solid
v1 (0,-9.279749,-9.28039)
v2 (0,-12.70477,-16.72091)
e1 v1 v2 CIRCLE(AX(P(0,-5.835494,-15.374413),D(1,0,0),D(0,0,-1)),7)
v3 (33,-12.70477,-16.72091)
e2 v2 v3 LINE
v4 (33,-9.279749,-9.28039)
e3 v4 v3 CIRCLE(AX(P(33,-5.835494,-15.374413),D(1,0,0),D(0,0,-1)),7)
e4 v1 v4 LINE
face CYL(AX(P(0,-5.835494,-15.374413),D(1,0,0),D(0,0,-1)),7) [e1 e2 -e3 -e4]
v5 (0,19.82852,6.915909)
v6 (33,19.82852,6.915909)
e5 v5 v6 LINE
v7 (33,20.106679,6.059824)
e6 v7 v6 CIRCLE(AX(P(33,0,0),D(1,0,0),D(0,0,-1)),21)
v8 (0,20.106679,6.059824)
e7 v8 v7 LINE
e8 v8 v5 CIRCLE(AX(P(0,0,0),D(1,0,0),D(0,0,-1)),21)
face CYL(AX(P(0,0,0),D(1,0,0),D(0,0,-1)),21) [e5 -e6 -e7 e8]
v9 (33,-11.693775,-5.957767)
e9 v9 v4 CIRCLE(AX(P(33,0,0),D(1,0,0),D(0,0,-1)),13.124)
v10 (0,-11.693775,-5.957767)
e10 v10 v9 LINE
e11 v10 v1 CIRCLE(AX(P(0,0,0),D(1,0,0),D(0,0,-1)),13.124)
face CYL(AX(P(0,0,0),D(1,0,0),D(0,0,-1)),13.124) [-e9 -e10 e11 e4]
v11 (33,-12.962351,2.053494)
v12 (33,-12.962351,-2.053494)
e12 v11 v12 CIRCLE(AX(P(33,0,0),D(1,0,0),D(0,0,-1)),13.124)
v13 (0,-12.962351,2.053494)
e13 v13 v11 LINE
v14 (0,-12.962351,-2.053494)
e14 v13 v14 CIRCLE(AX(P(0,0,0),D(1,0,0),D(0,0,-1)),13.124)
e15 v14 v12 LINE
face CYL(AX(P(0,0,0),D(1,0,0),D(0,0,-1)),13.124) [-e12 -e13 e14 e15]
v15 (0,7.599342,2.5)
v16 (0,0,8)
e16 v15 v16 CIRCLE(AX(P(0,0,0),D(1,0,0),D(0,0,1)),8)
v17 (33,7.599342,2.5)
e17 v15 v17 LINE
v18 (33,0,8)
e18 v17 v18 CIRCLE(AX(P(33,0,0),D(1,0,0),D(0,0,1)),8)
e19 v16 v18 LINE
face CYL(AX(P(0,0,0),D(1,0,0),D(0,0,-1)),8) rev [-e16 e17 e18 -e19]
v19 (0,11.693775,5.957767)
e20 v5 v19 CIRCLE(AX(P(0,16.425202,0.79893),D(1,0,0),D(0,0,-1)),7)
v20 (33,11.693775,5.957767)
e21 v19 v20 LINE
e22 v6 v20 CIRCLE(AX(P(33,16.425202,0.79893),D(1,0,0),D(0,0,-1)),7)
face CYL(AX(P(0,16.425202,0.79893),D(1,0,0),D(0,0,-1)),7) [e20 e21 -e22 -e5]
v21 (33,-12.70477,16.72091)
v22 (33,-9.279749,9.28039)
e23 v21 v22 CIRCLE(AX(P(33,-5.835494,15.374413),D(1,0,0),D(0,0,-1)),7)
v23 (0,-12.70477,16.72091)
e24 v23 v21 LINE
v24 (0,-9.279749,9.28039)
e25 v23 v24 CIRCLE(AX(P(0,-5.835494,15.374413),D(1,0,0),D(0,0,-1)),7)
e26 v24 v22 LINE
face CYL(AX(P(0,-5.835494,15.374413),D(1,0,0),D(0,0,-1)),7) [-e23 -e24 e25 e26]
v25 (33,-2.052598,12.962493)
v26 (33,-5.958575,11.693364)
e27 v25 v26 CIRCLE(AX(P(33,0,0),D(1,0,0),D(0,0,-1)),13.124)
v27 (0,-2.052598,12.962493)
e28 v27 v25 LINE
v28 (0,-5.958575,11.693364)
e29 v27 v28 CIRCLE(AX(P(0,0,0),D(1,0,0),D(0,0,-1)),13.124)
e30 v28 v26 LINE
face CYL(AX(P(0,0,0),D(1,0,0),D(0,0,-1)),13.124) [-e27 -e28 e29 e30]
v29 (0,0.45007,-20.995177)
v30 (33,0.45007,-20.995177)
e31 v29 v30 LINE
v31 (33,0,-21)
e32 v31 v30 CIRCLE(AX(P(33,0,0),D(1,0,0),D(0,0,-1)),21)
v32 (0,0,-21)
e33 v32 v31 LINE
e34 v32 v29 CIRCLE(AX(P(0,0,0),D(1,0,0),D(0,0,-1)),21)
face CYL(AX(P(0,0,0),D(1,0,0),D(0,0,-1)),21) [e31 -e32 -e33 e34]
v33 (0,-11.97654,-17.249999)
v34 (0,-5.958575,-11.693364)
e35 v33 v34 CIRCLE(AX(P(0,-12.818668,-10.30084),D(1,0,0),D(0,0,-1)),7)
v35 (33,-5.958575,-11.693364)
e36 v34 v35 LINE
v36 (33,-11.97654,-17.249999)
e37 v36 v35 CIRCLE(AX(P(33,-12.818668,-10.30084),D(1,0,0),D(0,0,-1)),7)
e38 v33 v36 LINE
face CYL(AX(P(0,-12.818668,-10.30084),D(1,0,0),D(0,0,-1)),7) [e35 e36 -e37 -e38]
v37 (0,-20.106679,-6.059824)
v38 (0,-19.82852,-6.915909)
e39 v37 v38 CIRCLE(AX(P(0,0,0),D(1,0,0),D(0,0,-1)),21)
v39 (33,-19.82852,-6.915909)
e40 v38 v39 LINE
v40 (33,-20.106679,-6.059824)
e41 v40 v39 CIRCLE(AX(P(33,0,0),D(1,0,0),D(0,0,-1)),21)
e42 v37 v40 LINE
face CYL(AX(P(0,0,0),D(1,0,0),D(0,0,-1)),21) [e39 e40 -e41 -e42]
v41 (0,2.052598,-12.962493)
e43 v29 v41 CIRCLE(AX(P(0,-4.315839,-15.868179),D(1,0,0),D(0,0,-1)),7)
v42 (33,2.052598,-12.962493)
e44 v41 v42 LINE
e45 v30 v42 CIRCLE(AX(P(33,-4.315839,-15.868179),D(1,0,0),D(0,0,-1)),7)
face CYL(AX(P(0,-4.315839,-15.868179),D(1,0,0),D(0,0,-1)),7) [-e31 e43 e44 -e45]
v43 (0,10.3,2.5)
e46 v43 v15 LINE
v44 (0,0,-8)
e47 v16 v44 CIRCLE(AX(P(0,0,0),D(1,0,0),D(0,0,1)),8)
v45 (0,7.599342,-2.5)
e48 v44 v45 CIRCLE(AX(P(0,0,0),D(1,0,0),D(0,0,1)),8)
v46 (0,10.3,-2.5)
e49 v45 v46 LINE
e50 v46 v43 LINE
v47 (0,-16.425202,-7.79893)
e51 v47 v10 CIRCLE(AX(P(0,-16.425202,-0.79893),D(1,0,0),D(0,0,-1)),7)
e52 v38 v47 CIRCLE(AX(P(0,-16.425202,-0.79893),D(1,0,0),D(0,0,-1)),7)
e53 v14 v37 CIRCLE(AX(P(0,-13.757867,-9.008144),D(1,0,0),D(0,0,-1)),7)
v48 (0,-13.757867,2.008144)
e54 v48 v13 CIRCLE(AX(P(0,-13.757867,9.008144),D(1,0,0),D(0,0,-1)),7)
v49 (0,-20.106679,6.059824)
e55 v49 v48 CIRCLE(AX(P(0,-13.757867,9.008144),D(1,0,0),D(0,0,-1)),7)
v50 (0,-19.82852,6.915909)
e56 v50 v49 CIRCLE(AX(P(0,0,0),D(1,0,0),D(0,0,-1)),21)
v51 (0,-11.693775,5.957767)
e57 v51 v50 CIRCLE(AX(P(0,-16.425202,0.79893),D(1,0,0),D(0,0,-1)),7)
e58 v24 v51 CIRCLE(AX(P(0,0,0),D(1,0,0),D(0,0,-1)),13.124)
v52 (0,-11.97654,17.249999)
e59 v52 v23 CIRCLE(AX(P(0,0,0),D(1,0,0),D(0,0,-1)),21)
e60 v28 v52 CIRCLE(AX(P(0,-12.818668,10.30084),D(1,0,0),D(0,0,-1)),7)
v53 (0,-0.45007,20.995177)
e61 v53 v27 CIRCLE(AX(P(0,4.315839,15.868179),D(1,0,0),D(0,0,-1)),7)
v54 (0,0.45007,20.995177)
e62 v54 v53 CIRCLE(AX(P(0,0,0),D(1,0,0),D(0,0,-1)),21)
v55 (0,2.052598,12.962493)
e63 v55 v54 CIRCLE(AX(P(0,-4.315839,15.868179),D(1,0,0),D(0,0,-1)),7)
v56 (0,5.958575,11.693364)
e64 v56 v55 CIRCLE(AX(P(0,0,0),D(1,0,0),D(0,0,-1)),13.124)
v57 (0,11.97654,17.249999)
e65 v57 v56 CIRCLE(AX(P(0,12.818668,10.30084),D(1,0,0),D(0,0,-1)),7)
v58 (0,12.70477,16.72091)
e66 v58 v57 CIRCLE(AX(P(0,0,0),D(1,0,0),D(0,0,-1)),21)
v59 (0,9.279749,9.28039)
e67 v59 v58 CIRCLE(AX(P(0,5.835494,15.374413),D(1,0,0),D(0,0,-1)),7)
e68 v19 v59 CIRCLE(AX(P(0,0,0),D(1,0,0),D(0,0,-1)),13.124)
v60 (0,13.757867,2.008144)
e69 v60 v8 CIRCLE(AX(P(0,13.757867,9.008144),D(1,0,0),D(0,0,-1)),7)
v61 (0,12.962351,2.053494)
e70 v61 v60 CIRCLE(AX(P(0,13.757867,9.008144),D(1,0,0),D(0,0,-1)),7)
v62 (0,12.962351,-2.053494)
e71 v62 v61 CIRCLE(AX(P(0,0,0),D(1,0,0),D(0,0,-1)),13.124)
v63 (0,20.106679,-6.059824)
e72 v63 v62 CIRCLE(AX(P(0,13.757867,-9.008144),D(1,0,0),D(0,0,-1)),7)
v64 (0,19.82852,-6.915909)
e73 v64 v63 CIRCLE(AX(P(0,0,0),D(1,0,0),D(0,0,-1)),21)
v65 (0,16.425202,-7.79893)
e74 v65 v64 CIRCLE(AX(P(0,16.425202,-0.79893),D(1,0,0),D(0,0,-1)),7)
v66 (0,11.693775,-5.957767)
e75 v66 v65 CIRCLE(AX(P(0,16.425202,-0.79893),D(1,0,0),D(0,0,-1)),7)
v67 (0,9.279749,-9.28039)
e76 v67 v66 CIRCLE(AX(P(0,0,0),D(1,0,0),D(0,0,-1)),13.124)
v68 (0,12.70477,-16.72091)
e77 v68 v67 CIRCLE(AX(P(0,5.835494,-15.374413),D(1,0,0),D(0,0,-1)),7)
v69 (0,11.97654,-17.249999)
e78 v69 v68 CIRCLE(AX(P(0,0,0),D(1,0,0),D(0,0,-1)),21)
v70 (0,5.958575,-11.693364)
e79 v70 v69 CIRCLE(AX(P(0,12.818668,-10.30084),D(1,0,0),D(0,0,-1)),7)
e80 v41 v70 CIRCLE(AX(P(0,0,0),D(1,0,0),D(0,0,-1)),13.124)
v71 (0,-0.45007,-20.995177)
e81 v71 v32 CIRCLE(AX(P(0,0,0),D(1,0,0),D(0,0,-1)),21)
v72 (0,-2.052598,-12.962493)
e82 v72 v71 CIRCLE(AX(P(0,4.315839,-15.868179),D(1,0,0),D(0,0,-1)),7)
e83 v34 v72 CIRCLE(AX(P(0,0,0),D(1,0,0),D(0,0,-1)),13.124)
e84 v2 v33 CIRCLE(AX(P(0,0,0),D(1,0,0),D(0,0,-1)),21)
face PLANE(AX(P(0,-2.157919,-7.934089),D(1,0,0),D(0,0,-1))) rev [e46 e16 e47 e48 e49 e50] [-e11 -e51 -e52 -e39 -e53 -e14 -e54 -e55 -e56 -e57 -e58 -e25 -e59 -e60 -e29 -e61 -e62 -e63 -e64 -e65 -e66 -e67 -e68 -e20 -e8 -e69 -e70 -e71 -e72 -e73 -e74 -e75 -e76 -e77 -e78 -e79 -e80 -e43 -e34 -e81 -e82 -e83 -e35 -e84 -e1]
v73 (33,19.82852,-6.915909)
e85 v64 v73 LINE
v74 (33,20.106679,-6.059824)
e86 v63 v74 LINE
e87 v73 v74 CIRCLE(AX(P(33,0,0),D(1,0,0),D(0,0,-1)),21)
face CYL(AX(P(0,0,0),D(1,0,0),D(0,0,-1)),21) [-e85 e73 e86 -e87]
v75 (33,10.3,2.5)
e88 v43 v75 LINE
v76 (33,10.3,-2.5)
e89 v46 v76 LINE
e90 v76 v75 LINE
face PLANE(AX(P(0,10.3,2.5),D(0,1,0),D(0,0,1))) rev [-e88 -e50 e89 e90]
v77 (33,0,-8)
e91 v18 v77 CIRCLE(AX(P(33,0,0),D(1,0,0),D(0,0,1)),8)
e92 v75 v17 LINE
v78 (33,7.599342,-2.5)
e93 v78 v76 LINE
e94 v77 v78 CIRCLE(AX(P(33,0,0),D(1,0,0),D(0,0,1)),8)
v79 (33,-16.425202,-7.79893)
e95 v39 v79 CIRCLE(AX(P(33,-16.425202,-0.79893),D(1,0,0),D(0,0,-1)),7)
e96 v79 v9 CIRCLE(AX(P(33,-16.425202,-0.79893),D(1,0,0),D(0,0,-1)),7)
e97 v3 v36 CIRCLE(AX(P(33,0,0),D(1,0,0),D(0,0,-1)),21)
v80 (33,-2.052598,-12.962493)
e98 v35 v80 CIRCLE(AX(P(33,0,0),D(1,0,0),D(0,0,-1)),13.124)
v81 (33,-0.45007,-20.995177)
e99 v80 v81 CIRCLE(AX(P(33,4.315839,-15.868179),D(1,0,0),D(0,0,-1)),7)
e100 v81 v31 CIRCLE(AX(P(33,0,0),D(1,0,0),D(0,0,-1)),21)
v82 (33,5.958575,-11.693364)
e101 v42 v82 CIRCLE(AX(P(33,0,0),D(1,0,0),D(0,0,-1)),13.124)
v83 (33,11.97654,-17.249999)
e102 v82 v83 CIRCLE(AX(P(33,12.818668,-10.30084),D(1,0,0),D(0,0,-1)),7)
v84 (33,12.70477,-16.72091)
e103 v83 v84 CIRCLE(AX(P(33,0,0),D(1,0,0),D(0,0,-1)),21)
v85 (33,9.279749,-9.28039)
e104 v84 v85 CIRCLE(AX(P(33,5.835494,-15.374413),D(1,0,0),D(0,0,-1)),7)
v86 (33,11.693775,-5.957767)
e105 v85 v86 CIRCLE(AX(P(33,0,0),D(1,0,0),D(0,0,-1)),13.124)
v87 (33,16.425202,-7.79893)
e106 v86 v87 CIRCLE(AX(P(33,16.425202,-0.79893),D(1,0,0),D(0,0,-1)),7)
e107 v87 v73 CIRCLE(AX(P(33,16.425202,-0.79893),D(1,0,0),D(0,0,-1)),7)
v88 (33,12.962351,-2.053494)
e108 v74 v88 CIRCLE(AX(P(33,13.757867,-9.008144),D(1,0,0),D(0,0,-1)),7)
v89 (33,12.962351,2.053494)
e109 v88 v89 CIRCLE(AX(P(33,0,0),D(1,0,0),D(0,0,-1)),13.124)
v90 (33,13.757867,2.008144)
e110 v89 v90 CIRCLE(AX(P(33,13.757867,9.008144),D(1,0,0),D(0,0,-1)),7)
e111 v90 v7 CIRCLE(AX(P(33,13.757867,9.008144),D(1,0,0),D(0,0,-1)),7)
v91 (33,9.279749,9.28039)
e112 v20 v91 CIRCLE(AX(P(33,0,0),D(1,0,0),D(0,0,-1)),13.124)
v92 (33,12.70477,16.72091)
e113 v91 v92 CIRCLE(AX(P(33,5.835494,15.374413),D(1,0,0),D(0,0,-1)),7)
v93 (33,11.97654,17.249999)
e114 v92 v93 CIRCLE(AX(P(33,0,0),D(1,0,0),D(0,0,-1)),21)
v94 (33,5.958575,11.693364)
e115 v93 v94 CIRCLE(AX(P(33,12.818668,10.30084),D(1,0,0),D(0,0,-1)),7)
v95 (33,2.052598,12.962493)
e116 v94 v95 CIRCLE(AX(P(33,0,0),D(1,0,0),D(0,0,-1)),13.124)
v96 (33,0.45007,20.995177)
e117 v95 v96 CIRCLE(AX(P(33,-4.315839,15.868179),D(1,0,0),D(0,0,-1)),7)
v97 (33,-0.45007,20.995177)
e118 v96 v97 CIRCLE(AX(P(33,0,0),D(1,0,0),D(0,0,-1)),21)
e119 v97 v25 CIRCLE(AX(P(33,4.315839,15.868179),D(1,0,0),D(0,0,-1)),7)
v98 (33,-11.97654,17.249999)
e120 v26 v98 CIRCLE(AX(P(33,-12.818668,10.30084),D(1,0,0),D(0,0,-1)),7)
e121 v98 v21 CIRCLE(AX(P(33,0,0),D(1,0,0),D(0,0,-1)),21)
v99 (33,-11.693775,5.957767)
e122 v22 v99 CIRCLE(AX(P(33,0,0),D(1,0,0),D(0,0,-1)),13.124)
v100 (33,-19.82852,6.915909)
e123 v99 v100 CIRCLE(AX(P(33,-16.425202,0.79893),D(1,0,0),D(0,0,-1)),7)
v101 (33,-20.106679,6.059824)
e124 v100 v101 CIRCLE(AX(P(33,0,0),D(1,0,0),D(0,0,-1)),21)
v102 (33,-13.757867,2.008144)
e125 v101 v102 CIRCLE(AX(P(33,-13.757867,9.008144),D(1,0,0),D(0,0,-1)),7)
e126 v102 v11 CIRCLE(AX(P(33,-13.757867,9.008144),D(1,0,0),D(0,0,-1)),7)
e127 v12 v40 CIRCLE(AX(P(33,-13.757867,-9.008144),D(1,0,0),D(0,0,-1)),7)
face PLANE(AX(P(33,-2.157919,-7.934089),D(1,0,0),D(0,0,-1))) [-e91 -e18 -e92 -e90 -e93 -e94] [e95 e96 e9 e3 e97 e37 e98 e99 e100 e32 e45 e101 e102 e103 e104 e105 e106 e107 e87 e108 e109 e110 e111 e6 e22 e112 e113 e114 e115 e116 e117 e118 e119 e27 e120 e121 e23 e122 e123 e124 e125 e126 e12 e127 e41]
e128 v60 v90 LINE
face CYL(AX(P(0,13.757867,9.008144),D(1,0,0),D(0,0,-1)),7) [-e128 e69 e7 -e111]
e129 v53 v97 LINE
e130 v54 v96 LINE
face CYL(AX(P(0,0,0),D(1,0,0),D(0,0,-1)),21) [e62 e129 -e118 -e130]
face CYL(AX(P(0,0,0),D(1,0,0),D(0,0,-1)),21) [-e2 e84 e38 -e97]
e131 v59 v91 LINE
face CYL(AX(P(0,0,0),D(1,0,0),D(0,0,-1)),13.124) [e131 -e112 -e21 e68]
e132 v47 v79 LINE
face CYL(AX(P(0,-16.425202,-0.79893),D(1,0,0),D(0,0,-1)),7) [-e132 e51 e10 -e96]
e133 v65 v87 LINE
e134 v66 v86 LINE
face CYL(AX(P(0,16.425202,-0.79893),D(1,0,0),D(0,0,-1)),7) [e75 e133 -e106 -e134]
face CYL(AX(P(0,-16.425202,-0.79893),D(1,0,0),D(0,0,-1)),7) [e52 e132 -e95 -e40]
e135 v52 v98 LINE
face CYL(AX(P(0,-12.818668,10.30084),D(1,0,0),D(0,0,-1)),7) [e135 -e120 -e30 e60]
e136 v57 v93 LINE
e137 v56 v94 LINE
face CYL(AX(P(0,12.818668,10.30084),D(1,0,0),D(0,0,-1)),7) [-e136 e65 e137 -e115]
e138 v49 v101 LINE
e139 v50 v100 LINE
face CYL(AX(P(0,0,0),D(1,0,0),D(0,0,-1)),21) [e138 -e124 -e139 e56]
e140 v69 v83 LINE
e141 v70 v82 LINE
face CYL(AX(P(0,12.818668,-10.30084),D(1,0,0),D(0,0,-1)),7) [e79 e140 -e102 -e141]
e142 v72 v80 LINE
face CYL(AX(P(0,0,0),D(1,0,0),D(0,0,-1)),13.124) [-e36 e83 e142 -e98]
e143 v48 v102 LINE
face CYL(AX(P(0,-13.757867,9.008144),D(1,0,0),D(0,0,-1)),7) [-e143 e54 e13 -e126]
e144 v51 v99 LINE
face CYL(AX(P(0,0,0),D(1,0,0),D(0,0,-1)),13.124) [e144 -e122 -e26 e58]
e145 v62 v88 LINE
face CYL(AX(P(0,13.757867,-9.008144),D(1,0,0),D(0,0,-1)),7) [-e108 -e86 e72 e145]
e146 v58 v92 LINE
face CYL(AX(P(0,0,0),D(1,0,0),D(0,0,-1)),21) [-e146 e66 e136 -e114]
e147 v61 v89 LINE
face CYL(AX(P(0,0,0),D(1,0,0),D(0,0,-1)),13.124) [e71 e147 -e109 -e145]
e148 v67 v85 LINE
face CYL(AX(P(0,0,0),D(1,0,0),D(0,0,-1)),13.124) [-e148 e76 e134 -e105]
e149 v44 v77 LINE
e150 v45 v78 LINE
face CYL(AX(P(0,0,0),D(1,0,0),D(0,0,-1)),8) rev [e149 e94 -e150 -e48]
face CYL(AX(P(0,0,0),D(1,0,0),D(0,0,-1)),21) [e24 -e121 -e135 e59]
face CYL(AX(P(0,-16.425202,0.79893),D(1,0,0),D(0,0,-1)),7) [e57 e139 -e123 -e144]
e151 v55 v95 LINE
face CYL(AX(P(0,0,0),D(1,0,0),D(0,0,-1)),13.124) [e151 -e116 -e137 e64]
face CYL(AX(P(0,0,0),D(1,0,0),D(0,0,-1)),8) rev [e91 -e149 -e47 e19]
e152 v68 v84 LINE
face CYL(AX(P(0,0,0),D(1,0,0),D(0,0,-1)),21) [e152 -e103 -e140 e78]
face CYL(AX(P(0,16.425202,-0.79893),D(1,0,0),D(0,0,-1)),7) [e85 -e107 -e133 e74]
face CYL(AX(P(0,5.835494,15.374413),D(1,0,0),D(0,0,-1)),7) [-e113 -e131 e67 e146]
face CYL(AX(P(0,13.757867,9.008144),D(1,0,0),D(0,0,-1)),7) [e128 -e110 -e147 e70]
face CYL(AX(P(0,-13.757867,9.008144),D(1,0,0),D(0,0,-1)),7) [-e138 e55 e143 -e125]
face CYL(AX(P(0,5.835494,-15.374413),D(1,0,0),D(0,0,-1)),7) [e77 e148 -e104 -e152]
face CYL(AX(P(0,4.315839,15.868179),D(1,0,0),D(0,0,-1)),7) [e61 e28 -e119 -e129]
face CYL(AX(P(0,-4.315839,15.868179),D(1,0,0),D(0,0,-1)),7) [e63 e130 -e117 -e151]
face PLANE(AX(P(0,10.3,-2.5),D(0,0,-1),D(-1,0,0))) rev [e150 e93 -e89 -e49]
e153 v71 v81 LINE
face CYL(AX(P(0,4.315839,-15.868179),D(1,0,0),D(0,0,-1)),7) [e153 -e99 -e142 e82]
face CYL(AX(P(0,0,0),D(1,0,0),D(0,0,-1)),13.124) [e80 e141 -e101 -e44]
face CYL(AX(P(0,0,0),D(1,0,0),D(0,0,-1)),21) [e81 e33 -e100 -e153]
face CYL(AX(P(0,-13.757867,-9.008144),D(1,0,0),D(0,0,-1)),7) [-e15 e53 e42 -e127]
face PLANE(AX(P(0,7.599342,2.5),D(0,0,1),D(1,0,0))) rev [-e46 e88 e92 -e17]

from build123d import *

# Parameters (mm, degrees)
BOSS_EXTRUDE1_DEPTH = 33


with BuildPart() as part:
    # Sketch1 → Boss-Extrude1 (new body)
    with BuildSketch(Plane(origin=(33, 0, 0), x_dir=(0, 0, -1), z_dir=(1, 0, 0))):
        with BuildLine():
            ThreePointArc((20.995176507, 0.450070465), (17.237696927, 2.548883943), (12.962492698, 2.05259812))
            ThreePointArc((12.962492698, 2.05259812), (12.48166572, 4.055539034), (11.693363786, 5.958575279))
            ThreePointArc((11.693363786, 5.958575279), (15.443786149, 8.06997361), (17.249999376, 11.976540465))
            ThreePointArc((17.249999376, 11.976540465), (16.989356882, 12.343490298), (16.720909812, 12.704769776))
            ThreePointArc((16.720909812, 12.704769776), (12.447393366, 12.194154464), (9.280389979, 9.279748803))
            ThreePointArc((9.280389979, 9.279748803), (7.714093651, 10.617539034), (5.957767351, 11.693775447))
            ThreePointArc((5.957767351, 11.693775447), (7.750873978, 15.606375533), (6.91590879, 19.828520006))
            ThreePointArc((6.91590879, 19.828520006), (6.489356882, 19.972186842), (6.059823892, 20.106678851))
            ThreePointArc((6.059823892, 20.106678851), (2.902608611, 17.181672443), (2.053493716, 12.96235085))
            ThreePointArc((2.053493716, 12.96235085), (0, 13.124), (-2.053493716, 12.96235085))
            ThreePointArc((-2.053493716, 12.96235085), (-2.902608611, 17.181672443), (-6.059823892, 20.106678851))
            ThreePointArc((-6.059823892, 20.106678851), (-6.489356882, 19.972186842), (-6.91590879, 19.828520006))
            ThreePointArc((-6.91590879, 19.828520006), (-7.750873978, 15.606375533), (-5.957767351, 11.693775447))
            ThreePointArc((-5.957767351, 11.693775447), (-7.714093651, 10.617539034), (-9.280389979, 9.279748803))
            ThreePointArc((-9.280389979, 9.279748803), (-12.447393366, 12.194154464), (-16.720909812, 12.704769776))
            ThreePointArc((-16.720909812, 12.704769776), (-16.989356882, 12.343490298), (-17.249999376, 11.976540465))
            ThreePointArc((-17.249999376, 11.976540465), (-15.443786149, 8.06997361), (-11.693363786, 5.958575279))
            ThreePointArc((-11.693363786, 5.958575279), (-12.48166572, 4.055539034), (-12.962492698, 2.05259812))
            ThreePointArc((-12.962492698, 2.05259812), (-17.237696927, 2.548883943), (-20.995176507, 0.450070465))
            ThreePointArc((-20.995176507, 0.450070465), (-21, 0), (-20.995176507, -0.450070465))
            ThreePointArc((-20.995176507, -0.450070465), (-17.237696927, -2.548883943), (-12.962492698, -2.05259812))
            ThreePointArc((-12.962492698, -2.05259812), (-12.48166572, -4.055539034), (-11.693363786, -5.958575279))
            ThreePointArc((-11.693363786, -5.958575279), (-15.443786149, -8.06997361), (-17.249999376, -11.976540465))
            ThreePointArc((-17.249999376, -11.976540465), (-16.989356882, -12.343490298), (-16.720909812, -12.704769776))
            ThreePointArc((-16.720909812, -12.704769776), (-12.447393366, -12.194154464), (-9.280389979, -9.279748803))
            ThreePointArc((-9.280389979, -9.279748803), (-7.714093651, -10.617539034), (-5.957767351, -11.693775447))
            ThreePointArc((-5.957767351, -11.693775447), (-7.750873978, -15.606375533), (-6.91590879, -19.828520006))
            ThreePointArc((-6.91590879, -19.828520006), (-6.489356882, -19.972186842), (-6.059823892, -20.106678851))
            ThreePointArc((-6.059823892, -20.106678851), (-2.902608611, -17.181672443), (-2.053493716, -12.96235085))
            ThreePointArc((-2.053493716, -12.96235085), (0, -13.124), (2.053493716, -12.96235085))
            ThreePointArc((2.053493716, -12.96235085), (2.902608611, -17.181672443), (6.059823892, -20.106678851))
            ThreePointArc((6.059823892, -20.106678851), (6.489356882, -19.972186842), (6.91590879, -19.828520006))
            ThreePointArc((6.91590879, -19.828520006), (7.750873978, -15.606375533), (5.957767351, -11.693775447))
            ThreePointArc((5.957767351, -11.693775447), (7.714093651, -10.617539034), (9.280389979, -9.279748803))
            ThreePointArc((9.280389979, -9.279748803), (12.447393366, -12.194154464), (16.720909812, -12.704769776))
            ThreePointArc((16.720909812, -12.704769776), (16.989356882, -12.343490298), (17.249999376, -11.976540465))
            ThreePointArc((17.249999376, -11.976540465), (15.443786149, -8.06997361), (11.693363786, -5.958575279))
            ThreePointArc((11.693363786, -5.958575279), (12.48166572, -4.055539034), (12.962492698, -2.05259812))
            ThreePointArc((12.962492698, -2.05259812), (17.237696927, -2.548883943), (20.995176507, -0.450070465))
            ThreePointArc((20.995176507, -0.450070465), (21, 0), (20.995176507, 0.450070465))
        make_face()
        with BuildLine():
            Line((2.5, 10.3), (2.5, 7.599342077))
            ThreePointArc((2.5, 7.599342077), (0, -8), (-2.5, 7.599342077))
            Line((-2.5, 7.599342077), (-2.5, 10.3))
            Line((-2.5, 10.3), (2.5, 10.3))
        make_face(mode=Mode.SUBTRACT)
    extrude(amount=-BOSS_EXTRUDE1_DEPTH)


solid = part.part
